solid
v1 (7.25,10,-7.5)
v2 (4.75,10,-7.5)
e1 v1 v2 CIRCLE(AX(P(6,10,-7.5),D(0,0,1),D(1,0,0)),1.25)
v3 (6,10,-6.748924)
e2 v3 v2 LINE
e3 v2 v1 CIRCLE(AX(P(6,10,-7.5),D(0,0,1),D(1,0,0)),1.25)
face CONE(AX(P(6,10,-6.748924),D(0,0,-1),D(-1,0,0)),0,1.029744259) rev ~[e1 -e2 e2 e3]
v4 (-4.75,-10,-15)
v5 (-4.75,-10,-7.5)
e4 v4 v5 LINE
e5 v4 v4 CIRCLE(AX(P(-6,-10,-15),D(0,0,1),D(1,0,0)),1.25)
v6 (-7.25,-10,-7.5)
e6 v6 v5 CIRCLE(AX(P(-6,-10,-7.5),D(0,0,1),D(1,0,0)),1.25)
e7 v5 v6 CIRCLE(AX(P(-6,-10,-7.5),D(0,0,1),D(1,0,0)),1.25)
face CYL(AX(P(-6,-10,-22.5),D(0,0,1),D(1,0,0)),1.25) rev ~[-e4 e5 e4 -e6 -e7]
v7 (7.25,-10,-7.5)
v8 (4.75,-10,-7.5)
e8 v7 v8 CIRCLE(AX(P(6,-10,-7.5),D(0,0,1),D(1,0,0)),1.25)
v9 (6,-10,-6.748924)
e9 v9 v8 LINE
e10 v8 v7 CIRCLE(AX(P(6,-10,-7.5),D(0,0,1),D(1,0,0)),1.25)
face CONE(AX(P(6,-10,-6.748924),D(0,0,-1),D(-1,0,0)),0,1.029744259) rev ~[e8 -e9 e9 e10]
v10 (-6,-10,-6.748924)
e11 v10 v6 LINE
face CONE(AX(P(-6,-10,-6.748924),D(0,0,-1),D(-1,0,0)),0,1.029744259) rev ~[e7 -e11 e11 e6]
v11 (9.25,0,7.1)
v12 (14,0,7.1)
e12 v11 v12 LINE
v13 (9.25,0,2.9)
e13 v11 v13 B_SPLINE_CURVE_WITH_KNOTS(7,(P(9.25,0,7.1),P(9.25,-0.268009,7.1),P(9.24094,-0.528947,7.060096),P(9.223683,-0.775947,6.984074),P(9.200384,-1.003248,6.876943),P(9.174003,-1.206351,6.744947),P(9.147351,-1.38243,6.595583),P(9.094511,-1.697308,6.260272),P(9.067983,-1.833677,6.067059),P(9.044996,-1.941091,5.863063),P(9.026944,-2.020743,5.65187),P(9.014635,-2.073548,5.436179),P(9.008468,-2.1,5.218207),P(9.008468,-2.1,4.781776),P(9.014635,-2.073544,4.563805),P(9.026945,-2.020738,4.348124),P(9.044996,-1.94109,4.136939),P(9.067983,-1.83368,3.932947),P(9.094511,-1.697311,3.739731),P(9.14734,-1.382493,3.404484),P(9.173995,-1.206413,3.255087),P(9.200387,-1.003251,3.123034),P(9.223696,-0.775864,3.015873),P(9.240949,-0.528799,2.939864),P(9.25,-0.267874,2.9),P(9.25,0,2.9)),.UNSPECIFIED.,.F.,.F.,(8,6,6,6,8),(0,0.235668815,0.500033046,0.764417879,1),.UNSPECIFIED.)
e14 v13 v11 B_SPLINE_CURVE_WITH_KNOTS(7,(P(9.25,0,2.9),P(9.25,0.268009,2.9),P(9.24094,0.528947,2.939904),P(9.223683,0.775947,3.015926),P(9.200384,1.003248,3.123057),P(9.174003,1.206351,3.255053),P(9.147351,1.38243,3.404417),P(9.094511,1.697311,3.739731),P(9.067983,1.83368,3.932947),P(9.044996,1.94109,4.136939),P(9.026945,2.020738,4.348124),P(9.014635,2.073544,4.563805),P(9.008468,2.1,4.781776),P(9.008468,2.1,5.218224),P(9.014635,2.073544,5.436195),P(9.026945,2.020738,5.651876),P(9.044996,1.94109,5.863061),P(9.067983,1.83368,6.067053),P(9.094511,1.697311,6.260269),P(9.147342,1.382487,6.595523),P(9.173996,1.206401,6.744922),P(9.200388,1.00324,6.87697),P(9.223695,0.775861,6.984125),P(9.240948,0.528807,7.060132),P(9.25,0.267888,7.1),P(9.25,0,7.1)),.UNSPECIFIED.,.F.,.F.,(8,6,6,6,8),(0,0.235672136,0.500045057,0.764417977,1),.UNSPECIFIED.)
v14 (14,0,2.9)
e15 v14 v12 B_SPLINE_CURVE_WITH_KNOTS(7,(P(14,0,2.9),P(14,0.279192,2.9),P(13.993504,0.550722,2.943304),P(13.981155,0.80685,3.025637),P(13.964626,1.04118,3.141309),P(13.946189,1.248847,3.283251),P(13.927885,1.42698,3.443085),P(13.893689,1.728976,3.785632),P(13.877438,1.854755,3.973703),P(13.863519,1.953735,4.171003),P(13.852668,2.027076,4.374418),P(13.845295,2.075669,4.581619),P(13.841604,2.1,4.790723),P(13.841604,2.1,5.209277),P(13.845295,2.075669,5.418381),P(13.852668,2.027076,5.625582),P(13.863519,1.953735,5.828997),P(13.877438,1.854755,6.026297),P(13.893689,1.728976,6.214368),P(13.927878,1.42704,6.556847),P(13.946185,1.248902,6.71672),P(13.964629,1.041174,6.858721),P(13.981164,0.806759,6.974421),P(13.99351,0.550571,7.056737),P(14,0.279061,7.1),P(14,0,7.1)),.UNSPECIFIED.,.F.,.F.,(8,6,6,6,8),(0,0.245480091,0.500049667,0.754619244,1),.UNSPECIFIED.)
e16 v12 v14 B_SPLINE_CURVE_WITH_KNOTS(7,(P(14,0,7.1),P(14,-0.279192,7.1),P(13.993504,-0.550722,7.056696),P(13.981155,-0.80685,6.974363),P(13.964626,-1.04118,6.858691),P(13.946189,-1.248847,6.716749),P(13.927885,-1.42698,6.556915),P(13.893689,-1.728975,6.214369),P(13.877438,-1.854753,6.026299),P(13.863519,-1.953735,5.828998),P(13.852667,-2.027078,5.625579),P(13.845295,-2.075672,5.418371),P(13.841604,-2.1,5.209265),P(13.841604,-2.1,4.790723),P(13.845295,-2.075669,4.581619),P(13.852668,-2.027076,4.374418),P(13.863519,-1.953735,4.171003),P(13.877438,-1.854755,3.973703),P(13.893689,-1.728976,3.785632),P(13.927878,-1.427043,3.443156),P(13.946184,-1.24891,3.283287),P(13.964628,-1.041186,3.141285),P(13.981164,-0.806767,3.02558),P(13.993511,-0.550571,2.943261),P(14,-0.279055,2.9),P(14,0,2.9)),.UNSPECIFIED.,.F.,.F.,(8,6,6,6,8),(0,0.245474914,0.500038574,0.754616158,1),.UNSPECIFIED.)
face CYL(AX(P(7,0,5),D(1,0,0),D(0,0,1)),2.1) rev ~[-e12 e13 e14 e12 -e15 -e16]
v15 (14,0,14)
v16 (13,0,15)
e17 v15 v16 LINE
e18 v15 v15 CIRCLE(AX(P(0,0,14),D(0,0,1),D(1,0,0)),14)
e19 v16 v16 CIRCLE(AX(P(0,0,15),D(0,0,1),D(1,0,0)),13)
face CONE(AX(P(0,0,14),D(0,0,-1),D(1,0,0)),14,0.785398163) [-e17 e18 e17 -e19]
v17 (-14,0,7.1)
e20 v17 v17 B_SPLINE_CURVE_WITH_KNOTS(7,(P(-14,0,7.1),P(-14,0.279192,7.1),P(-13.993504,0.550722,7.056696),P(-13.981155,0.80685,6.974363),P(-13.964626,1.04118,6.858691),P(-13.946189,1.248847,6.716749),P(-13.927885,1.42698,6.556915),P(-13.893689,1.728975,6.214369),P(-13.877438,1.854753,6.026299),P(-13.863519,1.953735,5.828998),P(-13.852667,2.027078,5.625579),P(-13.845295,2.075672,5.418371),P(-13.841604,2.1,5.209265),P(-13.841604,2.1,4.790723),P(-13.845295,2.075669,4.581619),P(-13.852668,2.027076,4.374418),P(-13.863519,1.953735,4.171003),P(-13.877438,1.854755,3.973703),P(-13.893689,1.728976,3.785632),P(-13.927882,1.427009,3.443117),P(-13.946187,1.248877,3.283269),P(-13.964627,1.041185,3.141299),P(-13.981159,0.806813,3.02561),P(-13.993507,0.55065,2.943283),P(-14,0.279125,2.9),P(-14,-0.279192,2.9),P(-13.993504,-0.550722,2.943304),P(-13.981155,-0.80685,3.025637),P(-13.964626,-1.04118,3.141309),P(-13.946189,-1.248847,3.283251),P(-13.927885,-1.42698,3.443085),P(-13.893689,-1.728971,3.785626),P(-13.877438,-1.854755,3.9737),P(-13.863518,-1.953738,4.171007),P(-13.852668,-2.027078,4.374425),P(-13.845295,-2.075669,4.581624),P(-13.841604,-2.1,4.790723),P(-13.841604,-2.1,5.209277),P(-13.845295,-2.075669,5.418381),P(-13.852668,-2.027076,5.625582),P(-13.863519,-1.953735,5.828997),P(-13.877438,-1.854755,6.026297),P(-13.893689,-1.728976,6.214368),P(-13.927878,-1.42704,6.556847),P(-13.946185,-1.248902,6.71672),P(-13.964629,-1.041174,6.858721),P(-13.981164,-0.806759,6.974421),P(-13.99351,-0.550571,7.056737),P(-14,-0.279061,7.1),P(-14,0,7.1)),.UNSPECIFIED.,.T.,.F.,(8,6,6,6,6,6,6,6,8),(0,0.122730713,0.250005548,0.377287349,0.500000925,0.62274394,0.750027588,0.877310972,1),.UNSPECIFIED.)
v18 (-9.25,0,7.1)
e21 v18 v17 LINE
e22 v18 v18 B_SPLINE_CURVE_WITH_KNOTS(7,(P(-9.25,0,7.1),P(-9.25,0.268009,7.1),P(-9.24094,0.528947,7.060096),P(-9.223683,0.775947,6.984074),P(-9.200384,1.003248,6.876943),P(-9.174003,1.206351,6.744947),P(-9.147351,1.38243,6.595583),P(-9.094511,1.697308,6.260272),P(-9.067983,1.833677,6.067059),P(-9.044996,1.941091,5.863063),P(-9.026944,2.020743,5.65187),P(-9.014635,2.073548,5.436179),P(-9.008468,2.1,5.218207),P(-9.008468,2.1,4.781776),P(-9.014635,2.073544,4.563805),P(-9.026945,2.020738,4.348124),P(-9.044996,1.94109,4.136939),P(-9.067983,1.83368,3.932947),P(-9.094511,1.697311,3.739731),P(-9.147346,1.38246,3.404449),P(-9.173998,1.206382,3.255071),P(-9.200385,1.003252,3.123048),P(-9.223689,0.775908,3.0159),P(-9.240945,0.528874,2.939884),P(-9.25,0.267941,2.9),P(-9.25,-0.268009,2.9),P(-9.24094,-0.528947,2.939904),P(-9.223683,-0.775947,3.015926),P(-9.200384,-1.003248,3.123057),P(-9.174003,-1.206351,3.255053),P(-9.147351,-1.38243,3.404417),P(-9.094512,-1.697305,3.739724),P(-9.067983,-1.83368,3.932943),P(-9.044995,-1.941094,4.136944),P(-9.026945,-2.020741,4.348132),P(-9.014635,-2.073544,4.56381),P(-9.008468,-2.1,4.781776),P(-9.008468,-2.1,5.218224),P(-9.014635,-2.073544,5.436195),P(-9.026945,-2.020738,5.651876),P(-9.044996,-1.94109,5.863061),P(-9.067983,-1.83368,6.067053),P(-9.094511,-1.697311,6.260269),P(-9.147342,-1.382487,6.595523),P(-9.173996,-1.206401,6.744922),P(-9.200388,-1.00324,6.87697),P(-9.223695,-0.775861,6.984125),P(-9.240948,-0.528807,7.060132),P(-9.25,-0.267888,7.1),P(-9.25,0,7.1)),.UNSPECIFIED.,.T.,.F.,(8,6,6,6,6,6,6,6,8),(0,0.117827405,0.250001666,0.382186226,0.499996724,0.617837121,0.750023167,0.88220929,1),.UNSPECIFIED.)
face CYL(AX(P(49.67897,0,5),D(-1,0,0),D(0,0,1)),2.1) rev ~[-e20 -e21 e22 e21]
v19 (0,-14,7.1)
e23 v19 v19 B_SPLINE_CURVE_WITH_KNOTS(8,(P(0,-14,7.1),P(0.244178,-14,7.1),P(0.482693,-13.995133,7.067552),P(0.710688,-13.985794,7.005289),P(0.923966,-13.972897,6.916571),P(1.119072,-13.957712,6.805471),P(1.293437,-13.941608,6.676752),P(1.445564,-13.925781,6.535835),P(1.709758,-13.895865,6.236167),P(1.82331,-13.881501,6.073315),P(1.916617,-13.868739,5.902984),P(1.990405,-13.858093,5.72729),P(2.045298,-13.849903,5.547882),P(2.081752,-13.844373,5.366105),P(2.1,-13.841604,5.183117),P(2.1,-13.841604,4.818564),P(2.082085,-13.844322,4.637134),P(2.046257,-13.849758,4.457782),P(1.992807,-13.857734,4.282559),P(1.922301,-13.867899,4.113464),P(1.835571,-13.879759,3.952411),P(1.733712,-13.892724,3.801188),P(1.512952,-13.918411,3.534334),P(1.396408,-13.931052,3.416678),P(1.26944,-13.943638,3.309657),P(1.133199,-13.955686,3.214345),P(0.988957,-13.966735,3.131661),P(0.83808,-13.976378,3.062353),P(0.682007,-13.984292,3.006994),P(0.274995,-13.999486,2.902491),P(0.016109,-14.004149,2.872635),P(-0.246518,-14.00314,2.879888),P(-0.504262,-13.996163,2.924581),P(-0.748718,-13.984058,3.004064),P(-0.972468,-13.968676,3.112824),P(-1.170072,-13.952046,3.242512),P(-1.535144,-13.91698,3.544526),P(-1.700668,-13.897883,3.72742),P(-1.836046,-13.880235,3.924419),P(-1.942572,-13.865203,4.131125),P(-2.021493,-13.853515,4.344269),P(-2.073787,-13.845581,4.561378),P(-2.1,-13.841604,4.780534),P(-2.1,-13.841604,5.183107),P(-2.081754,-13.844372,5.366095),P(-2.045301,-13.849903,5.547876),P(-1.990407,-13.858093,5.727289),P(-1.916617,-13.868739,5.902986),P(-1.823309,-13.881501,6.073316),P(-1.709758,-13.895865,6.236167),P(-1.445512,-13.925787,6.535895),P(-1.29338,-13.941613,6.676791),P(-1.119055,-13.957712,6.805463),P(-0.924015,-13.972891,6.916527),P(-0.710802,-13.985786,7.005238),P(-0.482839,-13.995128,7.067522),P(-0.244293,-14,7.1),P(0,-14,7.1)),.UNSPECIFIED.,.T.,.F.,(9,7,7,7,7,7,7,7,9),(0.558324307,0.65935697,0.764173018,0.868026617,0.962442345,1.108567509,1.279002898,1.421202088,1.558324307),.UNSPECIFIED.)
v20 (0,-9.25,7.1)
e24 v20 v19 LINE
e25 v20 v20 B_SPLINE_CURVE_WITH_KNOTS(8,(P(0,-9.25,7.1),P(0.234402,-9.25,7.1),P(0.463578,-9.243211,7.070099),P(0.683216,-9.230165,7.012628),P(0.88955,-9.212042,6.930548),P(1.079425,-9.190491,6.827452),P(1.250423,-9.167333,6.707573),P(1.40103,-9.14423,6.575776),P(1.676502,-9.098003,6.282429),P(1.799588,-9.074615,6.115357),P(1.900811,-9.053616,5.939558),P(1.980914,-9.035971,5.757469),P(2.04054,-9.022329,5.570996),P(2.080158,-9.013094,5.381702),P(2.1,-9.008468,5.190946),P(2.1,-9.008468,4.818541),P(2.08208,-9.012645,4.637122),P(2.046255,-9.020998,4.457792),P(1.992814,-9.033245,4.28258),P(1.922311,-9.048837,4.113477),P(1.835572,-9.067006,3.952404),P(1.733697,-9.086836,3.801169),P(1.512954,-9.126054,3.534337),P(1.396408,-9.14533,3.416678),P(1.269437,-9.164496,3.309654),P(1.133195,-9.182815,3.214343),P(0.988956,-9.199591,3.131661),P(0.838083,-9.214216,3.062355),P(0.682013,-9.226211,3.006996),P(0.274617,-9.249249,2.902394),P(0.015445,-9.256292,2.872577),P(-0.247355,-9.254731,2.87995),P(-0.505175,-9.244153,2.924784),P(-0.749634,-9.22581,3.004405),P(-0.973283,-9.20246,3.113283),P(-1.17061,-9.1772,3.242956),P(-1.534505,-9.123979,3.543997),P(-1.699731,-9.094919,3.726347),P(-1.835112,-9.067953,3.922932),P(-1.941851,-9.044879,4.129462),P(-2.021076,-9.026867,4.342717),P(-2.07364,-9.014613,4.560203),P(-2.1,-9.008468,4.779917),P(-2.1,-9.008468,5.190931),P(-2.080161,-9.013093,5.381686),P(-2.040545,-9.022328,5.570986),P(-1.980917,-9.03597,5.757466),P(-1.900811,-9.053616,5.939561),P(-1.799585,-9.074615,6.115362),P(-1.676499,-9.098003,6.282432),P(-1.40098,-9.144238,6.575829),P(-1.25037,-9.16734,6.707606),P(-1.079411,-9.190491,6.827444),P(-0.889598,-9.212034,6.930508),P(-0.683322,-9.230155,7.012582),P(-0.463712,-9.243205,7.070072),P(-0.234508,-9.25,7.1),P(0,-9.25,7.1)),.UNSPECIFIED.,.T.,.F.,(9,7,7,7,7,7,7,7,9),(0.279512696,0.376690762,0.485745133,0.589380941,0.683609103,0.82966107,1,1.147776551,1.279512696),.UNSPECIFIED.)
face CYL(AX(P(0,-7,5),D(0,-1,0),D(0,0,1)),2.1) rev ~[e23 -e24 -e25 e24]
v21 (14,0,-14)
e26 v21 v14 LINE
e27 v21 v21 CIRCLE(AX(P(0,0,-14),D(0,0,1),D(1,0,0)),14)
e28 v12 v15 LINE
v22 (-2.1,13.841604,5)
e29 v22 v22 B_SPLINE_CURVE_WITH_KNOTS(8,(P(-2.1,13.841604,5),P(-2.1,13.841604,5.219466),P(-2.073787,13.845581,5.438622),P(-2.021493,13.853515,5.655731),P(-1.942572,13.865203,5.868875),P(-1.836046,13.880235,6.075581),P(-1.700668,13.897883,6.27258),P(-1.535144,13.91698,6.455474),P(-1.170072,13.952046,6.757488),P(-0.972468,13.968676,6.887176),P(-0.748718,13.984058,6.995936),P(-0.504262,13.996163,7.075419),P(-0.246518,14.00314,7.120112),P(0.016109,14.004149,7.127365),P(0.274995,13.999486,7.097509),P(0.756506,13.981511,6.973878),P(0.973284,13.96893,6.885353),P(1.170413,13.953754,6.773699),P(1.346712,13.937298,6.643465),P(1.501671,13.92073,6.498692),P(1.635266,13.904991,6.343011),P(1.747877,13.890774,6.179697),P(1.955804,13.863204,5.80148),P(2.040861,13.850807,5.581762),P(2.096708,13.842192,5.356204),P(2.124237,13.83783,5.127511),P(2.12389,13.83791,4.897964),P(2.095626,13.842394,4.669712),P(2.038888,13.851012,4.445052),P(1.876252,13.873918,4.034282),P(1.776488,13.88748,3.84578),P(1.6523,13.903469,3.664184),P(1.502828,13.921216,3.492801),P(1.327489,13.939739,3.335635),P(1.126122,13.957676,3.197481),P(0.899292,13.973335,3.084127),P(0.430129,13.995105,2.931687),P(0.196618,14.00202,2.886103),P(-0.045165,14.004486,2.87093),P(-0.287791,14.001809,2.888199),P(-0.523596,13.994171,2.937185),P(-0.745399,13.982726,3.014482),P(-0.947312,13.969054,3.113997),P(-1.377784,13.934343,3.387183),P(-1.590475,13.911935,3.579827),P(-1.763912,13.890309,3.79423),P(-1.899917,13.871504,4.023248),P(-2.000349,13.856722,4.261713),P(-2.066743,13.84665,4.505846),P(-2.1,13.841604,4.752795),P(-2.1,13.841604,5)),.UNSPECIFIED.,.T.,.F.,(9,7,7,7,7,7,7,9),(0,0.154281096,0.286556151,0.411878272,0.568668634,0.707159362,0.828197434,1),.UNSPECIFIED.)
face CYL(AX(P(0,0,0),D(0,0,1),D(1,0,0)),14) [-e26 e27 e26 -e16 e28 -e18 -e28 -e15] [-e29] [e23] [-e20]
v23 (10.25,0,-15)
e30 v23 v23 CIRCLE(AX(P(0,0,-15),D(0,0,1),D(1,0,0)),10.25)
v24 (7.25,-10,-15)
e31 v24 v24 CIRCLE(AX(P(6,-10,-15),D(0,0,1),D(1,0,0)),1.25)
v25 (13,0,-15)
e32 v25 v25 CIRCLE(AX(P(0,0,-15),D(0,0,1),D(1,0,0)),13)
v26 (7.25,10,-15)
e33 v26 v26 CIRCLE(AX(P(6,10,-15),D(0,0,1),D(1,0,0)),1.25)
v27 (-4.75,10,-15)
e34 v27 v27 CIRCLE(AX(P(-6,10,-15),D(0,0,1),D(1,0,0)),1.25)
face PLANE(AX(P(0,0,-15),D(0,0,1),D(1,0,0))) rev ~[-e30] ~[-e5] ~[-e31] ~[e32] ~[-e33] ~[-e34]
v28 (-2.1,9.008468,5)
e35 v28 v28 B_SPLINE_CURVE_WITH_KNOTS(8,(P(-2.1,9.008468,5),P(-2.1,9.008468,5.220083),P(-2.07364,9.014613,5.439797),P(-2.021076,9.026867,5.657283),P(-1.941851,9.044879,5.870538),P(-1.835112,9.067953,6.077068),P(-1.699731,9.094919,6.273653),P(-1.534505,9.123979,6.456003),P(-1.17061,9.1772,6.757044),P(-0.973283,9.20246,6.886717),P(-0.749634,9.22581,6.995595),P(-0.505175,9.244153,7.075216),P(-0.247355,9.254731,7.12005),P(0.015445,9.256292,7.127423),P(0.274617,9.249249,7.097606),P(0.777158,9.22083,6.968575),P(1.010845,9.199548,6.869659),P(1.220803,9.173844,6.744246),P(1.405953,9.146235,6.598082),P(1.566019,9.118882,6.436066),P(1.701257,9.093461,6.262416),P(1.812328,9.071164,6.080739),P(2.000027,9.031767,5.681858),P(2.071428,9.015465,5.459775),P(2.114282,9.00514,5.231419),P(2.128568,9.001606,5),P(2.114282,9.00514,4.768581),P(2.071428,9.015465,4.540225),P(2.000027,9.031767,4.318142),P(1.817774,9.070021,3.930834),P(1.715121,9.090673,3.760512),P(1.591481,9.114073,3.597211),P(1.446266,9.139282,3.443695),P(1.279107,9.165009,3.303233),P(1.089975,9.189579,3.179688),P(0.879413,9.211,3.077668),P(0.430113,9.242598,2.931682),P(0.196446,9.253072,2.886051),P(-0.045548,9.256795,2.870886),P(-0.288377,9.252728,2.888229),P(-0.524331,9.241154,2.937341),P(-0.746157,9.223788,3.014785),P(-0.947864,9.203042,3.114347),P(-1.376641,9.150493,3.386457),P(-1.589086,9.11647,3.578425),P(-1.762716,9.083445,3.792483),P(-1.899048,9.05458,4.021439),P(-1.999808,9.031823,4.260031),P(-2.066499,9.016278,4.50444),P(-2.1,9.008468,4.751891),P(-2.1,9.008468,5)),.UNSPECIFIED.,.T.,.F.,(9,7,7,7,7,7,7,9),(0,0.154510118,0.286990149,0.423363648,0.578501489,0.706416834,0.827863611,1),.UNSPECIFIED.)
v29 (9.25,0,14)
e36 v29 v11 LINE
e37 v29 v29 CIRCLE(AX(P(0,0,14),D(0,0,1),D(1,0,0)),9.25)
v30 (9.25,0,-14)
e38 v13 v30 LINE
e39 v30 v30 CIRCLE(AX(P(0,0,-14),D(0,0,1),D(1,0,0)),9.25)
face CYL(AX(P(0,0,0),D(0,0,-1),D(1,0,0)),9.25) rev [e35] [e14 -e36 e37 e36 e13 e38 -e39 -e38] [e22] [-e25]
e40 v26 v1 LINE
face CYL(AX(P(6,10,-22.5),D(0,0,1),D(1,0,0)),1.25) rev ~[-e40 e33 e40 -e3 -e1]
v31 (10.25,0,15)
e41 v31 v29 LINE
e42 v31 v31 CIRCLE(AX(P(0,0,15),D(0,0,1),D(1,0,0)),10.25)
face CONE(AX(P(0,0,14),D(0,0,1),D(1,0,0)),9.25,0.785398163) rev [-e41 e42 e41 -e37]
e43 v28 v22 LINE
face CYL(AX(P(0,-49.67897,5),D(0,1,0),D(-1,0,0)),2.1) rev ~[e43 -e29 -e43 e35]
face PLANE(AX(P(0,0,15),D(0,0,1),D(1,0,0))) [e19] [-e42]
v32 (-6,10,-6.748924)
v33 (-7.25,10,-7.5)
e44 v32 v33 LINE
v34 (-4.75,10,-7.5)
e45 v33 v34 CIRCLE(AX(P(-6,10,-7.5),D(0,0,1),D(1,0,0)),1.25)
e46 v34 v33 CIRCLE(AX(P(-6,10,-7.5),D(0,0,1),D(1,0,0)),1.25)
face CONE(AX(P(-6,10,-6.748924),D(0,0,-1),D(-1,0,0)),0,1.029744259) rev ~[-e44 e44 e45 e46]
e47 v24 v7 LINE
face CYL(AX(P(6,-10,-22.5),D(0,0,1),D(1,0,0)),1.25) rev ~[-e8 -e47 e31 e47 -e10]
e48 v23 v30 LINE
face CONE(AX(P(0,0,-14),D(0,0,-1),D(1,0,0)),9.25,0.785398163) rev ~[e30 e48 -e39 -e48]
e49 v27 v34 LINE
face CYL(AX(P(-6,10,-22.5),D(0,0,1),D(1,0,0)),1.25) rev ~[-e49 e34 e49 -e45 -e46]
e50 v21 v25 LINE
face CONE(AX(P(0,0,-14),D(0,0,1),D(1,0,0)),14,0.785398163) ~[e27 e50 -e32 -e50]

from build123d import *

# Parameters (mm, degrees)
SKETCH1_R             = 14
SKETCH1_R_2           = 9.25
BOSS_EXTRUDE1_DEPTH   = 15
SKETCH2_W             = 2.1
SKETCH2_H             = 14
SKETCH4_W             = 2.1
SKETCH4_H             = 14
M5_TAPPED_HOLE3_D     = 4.2
M5_TAPPED_HOLE4_D     = 4.2
M3_TAPPED_HOLE1_D     = 2.5
M3_TAPPED_HOLE1_DEPTH = 7.5
M3_TAPPED_HOLE1_TIP   = 0.751075774
CHAMFER1_SIZE         = 1


with BuildPart() as part:
    # Sketch1 → Boss-Extrude1 (new, symmetric)
    with BuildSketch(Plane.XY):
        Circle(SKETCH1_R)
        Circle(SKETCH1_R_2, mode=Mode.SUBTRACT)
    extrude(amount=BOSS_EXTRUDE1_DEPTH, both=True)

    # Sketch2 → M5 Tapped Hole1 (revolve, cut)
    with BuildSketch(Plane(origin=(0, 0, 5), x_dir=(0, 0, 1), z_dir=(1, 0, 0))):
        with Locations((1.05, 7)):
            Rectangle(SKETCH2_W, SKETCH2_H)
    revolve(axis=Axis((0, 6.35, 5), (0, -1, 0)), mode=Mode.SUBTRACT)

    # Sketch4 → M5 Tapped Hole2 (revolve, cut)
    with BuildSketch(Plane(origin=(0, 0, 5), x_dir=(0, 0, 1), z_dir=(0, 1, 0))):
        with Locations((1.05, 7)):
            Rectangle(SKETCH4_W, SKETCH4_H)
    revolve(axis=Axis((-6.35, 0, 5), (1, 0, 0)), mode=Mode.SUBTRACT)

    # M5 Tapped Hole3 (through all)
    with Locations(Plane.XZ):
        with Locations((0, 5)):
            Hole(M5_TAPPED_HOLE3_D / 2)

    # M5 Tapped Hole4 (through all)
    with Locations(Plane(origin=(0, 0, 0), x_dir=(0, 0, -1), z_dir=(1, 0, 0))):
        with Locations((-5, 0)):
            Hole(M5_TAPPED_HOLE4_D / 2)

    # M3 Tapped Hole1
    with Locations(Plane(origin=(0, 0, -15), x_dir=(-1, 0, 0), z_dir=(0, 0, -1))):
        with Locations((6, 10), (6, -10), (-6, -10), (-6, 10)):
            Hole(M3_TAPPED_HOLE1_D / 2, depth=M3_TAPPED_HOLE1_DEPTH)
            with Locations((0, 0, -(M3_TAPPED_HOLE1_DEPTH + M3_TAPPED_HOLE1_TIP / 2))):  # 118° drill point
                Cone(0, M3_TAPPED_HOLE1_D / 2, M3_TAPPED_HOLE1_TIP, mode=Mode.SUBTRACT)

    # Chamfer1
    chamfer1_edges = [part.edges().sort_by_distance(p)[0] for p in [
        (-14, 0, -15),
        (-14, 0, 15),
        (-9.25, 0, -15),
        (-9.25, 0, 15),
    ]]
    chamfer(chamfer1_edges, length=CHAMFER1_SIZE)


solid = part.part
